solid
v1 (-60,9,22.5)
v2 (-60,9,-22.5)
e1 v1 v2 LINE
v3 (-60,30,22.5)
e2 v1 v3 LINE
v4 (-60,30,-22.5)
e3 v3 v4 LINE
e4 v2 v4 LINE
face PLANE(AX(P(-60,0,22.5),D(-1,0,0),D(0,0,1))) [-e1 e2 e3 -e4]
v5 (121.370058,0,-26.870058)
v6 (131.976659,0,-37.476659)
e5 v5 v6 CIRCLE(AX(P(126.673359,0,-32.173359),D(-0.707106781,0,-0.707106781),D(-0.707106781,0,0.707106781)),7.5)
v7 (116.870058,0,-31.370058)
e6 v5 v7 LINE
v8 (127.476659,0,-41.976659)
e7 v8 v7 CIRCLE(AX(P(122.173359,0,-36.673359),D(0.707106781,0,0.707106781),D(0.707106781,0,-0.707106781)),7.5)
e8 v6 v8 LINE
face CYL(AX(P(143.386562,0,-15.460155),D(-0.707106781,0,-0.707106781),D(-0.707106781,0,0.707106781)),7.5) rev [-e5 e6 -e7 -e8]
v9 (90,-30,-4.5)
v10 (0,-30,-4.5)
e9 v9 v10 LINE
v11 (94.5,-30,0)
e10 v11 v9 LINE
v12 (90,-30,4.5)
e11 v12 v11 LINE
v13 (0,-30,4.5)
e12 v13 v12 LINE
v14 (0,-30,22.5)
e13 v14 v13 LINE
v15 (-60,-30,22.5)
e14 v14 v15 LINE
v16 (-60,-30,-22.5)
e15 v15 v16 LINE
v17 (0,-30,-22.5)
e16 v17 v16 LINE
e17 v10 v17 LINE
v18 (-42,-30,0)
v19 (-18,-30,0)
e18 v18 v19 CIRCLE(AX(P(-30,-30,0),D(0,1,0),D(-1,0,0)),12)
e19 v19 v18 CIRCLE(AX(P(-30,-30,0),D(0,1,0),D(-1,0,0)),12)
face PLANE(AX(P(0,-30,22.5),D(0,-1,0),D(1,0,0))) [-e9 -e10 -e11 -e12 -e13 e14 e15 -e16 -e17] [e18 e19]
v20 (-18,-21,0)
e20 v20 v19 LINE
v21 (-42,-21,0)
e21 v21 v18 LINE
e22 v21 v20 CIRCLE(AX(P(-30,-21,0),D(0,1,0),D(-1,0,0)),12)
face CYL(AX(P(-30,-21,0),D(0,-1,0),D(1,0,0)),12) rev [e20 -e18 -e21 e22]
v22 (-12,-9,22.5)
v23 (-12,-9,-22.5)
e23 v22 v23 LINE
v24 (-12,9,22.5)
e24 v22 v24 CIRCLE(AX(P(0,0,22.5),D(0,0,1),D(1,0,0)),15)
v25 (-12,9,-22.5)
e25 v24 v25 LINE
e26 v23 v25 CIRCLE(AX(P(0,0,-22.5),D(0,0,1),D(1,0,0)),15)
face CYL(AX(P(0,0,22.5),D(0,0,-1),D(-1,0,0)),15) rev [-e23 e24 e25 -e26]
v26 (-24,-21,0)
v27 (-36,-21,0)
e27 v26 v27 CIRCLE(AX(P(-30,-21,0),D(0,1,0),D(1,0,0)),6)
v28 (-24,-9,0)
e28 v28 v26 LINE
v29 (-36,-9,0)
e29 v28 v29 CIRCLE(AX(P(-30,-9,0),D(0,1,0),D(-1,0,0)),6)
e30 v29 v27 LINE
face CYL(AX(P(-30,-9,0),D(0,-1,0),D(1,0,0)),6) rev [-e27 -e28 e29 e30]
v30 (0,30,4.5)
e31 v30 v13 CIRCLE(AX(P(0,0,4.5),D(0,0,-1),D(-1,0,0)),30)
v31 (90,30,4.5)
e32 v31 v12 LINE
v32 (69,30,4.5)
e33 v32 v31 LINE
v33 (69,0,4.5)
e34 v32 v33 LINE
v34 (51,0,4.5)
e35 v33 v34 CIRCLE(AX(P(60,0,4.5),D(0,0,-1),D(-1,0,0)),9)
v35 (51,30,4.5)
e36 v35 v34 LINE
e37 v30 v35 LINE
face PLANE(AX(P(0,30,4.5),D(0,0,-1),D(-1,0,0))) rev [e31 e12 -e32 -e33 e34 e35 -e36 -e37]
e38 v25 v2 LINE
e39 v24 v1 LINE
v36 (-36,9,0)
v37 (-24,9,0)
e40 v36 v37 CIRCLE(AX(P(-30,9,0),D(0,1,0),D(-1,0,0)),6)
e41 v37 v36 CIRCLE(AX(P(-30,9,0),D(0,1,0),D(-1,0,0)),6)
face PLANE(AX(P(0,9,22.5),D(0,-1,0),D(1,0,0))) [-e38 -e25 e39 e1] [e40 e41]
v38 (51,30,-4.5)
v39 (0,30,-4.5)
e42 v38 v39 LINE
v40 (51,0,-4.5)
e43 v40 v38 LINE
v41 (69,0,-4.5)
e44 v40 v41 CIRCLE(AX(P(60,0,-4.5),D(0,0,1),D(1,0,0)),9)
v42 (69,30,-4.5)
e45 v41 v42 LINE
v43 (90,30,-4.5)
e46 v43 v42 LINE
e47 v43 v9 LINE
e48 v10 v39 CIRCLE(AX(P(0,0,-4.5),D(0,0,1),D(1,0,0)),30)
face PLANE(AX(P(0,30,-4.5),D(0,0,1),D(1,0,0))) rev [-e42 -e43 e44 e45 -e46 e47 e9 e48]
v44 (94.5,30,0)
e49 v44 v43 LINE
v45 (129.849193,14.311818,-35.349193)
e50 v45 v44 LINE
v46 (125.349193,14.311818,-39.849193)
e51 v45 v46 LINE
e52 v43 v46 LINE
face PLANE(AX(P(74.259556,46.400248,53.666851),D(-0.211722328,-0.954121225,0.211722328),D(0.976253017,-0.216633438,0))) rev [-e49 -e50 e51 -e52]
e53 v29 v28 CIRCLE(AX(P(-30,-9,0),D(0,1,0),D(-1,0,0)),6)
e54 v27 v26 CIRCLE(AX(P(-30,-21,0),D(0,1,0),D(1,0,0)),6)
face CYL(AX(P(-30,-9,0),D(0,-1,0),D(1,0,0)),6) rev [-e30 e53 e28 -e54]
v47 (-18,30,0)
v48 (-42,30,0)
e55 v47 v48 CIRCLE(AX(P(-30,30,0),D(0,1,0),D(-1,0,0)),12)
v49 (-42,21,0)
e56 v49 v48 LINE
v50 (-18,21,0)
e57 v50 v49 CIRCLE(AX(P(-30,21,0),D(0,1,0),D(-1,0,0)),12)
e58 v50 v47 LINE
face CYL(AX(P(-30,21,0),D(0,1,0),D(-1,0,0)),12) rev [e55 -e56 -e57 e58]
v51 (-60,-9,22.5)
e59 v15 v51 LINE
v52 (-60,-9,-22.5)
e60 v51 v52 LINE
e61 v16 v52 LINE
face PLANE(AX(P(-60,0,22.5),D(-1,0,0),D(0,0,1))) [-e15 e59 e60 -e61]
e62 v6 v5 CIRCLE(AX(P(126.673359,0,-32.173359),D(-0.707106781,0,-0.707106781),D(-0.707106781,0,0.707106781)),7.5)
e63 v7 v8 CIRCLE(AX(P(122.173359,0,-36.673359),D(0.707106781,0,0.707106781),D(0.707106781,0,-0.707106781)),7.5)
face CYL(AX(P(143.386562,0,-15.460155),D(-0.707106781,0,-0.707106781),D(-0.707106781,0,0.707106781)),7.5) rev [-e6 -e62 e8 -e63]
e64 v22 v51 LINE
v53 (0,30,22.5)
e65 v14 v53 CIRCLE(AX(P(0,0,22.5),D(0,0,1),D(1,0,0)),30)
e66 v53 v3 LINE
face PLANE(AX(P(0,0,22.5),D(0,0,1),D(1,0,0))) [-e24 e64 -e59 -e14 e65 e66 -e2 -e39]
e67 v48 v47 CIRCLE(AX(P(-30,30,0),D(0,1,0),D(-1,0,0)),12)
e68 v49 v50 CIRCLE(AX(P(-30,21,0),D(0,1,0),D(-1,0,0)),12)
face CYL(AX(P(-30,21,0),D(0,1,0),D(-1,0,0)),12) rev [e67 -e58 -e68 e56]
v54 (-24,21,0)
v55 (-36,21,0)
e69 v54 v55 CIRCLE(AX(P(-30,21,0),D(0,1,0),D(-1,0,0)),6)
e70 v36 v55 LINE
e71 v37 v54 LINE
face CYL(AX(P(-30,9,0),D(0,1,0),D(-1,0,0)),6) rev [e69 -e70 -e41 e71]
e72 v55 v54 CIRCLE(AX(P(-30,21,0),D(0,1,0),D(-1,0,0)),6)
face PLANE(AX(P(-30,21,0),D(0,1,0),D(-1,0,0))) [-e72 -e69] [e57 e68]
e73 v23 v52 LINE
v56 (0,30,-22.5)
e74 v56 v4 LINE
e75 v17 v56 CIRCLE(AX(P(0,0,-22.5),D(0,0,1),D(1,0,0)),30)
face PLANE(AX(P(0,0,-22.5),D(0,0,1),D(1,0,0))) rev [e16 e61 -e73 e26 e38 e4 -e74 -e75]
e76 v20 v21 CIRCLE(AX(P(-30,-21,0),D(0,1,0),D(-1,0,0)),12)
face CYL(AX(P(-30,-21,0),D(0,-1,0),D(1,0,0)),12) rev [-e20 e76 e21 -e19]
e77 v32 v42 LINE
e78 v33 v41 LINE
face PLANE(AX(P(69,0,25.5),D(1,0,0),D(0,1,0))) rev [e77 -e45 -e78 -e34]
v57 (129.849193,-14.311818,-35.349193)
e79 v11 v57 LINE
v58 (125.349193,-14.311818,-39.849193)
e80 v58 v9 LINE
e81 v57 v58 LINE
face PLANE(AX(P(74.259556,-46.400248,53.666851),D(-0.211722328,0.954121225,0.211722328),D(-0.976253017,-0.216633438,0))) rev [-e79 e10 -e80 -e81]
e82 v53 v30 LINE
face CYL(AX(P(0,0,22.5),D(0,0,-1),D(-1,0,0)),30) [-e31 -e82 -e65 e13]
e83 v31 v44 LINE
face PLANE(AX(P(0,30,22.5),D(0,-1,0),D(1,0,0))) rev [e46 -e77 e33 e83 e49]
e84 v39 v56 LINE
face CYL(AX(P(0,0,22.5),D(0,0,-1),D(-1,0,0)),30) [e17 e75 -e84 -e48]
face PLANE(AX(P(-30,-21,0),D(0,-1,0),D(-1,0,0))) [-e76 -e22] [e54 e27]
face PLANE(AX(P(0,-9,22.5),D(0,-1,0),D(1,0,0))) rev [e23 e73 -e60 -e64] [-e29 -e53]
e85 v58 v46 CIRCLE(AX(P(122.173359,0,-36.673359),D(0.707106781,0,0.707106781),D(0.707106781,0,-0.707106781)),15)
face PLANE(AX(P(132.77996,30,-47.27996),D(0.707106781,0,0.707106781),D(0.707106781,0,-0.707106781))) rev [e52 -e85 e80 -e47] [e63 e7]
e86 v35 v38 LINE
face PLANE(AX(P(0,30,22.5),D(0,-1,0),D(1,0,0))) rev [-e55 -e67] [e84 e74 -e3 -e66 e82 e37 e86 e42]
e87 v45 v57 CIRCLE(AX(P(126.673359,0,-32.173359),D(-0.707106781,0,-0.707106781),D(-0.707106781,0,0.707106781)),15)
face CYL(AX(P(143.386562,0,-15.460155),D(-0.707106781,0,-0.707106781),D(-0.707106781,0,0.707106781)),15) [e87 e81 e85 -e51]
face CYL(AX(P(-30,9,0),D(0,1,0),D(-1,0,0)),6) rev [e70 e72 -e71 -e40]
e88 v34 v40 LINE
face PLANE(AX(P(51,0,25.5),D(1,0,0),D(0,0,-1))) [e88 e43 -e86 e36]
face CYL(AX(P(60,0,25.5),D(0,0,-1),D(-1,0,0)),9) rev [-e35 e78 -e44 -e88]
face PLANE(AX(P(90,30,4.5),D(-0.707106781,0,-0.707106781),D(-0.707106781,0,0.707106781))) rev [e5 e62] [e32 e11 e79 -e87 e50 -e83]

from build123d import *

# Parameters (mm, degrees)
CLEVIS_BLOCK_DEPTH         = 22.5
COUNTERBORE_SKETCH_R       = 12
PIN_HOLE_COUNTERBORE_DEPTH = 9
PIN_HOLE_SKETCH_R          = 6
PIN_HOLE_12_DEPTH          = 21
MOUNTING_ARM_DEPTH         = 30
ARM_CLEARANCE_CUT_DEPTH    = 30
EYE_PROFILE_CUT_DEPTH      = 30
EYE_BORE_SKETCH_R          = 7.5
EYE_BORE_DEPTH             = 30
RELIEF_SLOT_CUT_DEPTH      = 148.549271396
RELIEF_SLOT_CUT_DEPTH_BACK = 148.549271396


with BuildPart() as part:
    # Clevis Block Sketch → Clevis Block (new, symmetric)
    with BuildSketch(Plane.XY):
        with BuildLine():
            Line((0, -30), (-60, -30))
            Line((-60, -30), (-60, -9))
            Line((-60, -9), (-28.618176043, -9))
            Line((-28.618176043, -9), (-12, -9))
            ThreePointArc((-12, -9), (15, 0), (-12, 9))
            Line((-12, 9), (-28.618176043, 9))
            Line((-28.618176043, 9), (-60, 9))
            Line((-60, 9), (-60, 30))
            Line((-60, 30), (0, 30))
            ThreePointArc((0, 30), (30, 0), (0, -30))
        make_face()
    extrude(amount=CLEVIS_BLOCK_DEPTH, both=True)

    # Counterbore Sketch → Pin Hole Counterbore (cut)
    with BuildSketch(Plane(origin=(0, 30, 0), x_dir=(1, 0, 0), z_dir=(0, 1, 0))):
        with Locations(Location((-30, 0, 0), (0, 0, 180))):
            Circle(COUNTERBORE_SKETCH_R)
    pin_hole_counterbore = extrude(amount=-PIN_HOLE_COUNTERBORE_DEPTH, mode=Mode.SUBTRACT)

    # Pin Hole Sketch → Pin Hole Ø12 (cut)
    with BuildSketch(Plane(origin=(0, 30, 0), x_dir=(1, 0, 0), z_dir=(0, 1, 0))):
        with Locations(Location((-30, 0, 0), (0, 0, 180))):
            Circle(PIN_HOLE_SKETCH_R)
    pin_hole_12 = extrude(amount=-PIN_HOLE_12_DEPTH, mode=Mode.SUBTRACT)

    # Counterbore Mirror: Pin Hole Counterbore across plane
    add(pin_hole_counterbore.mirror(Plane.ZX), mode=Mode.SUBTRACT)

    # Pin Hole Mirror: Pin Hole Ø12 across plane
    add(pin_hole_12.mirror(Plane.ZX), mode=Mode.SUBTRACT)

    # Mounting Arm Sketch → Mounting Arm (add, symmetric)
    with BuildSketch(Plane(origin=(0, 0, 0), x_dir=(1, 0, 0), z_dir=(0, 1, 0))):
        Polygon((0, -4.5), (90, -4.5), (137.279960262, 42.779960262), (132.779960262, 47.279960262), (90, 4.5), (0, 4.5), align=None)
    extrude(amount=MOUNTING_ARM_DEPTH, both=True)

    # Arm Clearance Cut Sketch → Arm Clearance Cut (cut, symmetric)
    with BuildSketch(Plane(origin=(0, 0, -4.5), x_dir=(-1, 0, 0), z_dir=(0, 0, -1))):
        with BuildLine():
            Line((-51, 21), (-51, 30))
            Line((-51, 30), (-60, 30))
            Line((-60, 30), (-69, 30))
            Line((-69, 30), (-69, 0))
            ThreePointArc((-69, 0), (-60, -9), (-51, 0))
            Line((-51, 0), (-51, 21))
        make_face()
    extrude(amount=ARM_CLEARANCE_CUT_DEPTH, both=True, mode=Mode.SUBTRACT)

    # Eye Profile Cut Sketch → Eye Profile Cut (cut, symmetric)
    with BuildSketch(Plane(origin=(42.75, 0, 42.75), x_dir=(-0.7071067811865513, 0, 0.7071067811865437), z_dir=(-0.7071067811865437, 0, -0.7071067811865513))):
        with BuildLine():
            Line((-127.321590822, 30), (-127.321590822, 0))
            ThreePointArc((-127.321590822, 0), (-124.412282123, 8.87779161), (-116.812899639, 14.311818372))
            Line((-116.812899639, 14.311818372), (-66.821590822, 30))
            Line((-66.821590822, 30), (-127.321590822, 30))
        make_face()
        with BuildLine():
            ThreePointArc((-116.812899639, -14.311818372), (-124.412282123, -8.87779161), (-127.321590822, 0))
            Line((-127.321590822, 0), (-127.321590822, -30))
            Line((-127.321590822, -30), (-66.821590822, -30))
            Line((-66.821590822, -30), (-116.812899639, -14.311818372))
        make_face()
    extrude(amount=EYE_PROFILE_CUT_DEPTH, both=True, mode=Mode.SUBTRACT)

    # Eye Bore Sketch → Eye Bore (cut, symmetric)
    with BuildSketch(Plane(origin=(42.75, 0, 42.75), x_dir=(-0.7071067811865513, 0, 0.7071067811865437), z_dir=(-0.7071067811865437, 0, -0.7071067811865513))):
        with Locations((-112.321590822, 0)):
            Circle(EYE_BORE_SKETCH_R)
    extrude(amount=EYE_BORE_DEPTH, both=True, mode=Mode.SUBTRACT)

    # Relief Slot Sketch → Relief Slot Cut (cut, two sides: drawn at the far end of the back side and taken through both)
    with BuildSketch(Plane(origin=(0, 0, -22.5), x_dir=(-1, 0, 0), z_dir=(0, 0, -1)).offset(-RELIEF_SLOT_CUT_DEPTH_BACK)):
        with BuildLine():
            Line((0, 15), (0, -15))
            ThreePointArc((0, -15), (-15, 0), (0, 15))
        make_face()
    extrude(amount=RELIEF_SLOT_CUT_DEPTH + RELIEF_SLOT_CUT_DEPTH_BACK, mode=Mode.SUBTRACT)


solid = part.part
